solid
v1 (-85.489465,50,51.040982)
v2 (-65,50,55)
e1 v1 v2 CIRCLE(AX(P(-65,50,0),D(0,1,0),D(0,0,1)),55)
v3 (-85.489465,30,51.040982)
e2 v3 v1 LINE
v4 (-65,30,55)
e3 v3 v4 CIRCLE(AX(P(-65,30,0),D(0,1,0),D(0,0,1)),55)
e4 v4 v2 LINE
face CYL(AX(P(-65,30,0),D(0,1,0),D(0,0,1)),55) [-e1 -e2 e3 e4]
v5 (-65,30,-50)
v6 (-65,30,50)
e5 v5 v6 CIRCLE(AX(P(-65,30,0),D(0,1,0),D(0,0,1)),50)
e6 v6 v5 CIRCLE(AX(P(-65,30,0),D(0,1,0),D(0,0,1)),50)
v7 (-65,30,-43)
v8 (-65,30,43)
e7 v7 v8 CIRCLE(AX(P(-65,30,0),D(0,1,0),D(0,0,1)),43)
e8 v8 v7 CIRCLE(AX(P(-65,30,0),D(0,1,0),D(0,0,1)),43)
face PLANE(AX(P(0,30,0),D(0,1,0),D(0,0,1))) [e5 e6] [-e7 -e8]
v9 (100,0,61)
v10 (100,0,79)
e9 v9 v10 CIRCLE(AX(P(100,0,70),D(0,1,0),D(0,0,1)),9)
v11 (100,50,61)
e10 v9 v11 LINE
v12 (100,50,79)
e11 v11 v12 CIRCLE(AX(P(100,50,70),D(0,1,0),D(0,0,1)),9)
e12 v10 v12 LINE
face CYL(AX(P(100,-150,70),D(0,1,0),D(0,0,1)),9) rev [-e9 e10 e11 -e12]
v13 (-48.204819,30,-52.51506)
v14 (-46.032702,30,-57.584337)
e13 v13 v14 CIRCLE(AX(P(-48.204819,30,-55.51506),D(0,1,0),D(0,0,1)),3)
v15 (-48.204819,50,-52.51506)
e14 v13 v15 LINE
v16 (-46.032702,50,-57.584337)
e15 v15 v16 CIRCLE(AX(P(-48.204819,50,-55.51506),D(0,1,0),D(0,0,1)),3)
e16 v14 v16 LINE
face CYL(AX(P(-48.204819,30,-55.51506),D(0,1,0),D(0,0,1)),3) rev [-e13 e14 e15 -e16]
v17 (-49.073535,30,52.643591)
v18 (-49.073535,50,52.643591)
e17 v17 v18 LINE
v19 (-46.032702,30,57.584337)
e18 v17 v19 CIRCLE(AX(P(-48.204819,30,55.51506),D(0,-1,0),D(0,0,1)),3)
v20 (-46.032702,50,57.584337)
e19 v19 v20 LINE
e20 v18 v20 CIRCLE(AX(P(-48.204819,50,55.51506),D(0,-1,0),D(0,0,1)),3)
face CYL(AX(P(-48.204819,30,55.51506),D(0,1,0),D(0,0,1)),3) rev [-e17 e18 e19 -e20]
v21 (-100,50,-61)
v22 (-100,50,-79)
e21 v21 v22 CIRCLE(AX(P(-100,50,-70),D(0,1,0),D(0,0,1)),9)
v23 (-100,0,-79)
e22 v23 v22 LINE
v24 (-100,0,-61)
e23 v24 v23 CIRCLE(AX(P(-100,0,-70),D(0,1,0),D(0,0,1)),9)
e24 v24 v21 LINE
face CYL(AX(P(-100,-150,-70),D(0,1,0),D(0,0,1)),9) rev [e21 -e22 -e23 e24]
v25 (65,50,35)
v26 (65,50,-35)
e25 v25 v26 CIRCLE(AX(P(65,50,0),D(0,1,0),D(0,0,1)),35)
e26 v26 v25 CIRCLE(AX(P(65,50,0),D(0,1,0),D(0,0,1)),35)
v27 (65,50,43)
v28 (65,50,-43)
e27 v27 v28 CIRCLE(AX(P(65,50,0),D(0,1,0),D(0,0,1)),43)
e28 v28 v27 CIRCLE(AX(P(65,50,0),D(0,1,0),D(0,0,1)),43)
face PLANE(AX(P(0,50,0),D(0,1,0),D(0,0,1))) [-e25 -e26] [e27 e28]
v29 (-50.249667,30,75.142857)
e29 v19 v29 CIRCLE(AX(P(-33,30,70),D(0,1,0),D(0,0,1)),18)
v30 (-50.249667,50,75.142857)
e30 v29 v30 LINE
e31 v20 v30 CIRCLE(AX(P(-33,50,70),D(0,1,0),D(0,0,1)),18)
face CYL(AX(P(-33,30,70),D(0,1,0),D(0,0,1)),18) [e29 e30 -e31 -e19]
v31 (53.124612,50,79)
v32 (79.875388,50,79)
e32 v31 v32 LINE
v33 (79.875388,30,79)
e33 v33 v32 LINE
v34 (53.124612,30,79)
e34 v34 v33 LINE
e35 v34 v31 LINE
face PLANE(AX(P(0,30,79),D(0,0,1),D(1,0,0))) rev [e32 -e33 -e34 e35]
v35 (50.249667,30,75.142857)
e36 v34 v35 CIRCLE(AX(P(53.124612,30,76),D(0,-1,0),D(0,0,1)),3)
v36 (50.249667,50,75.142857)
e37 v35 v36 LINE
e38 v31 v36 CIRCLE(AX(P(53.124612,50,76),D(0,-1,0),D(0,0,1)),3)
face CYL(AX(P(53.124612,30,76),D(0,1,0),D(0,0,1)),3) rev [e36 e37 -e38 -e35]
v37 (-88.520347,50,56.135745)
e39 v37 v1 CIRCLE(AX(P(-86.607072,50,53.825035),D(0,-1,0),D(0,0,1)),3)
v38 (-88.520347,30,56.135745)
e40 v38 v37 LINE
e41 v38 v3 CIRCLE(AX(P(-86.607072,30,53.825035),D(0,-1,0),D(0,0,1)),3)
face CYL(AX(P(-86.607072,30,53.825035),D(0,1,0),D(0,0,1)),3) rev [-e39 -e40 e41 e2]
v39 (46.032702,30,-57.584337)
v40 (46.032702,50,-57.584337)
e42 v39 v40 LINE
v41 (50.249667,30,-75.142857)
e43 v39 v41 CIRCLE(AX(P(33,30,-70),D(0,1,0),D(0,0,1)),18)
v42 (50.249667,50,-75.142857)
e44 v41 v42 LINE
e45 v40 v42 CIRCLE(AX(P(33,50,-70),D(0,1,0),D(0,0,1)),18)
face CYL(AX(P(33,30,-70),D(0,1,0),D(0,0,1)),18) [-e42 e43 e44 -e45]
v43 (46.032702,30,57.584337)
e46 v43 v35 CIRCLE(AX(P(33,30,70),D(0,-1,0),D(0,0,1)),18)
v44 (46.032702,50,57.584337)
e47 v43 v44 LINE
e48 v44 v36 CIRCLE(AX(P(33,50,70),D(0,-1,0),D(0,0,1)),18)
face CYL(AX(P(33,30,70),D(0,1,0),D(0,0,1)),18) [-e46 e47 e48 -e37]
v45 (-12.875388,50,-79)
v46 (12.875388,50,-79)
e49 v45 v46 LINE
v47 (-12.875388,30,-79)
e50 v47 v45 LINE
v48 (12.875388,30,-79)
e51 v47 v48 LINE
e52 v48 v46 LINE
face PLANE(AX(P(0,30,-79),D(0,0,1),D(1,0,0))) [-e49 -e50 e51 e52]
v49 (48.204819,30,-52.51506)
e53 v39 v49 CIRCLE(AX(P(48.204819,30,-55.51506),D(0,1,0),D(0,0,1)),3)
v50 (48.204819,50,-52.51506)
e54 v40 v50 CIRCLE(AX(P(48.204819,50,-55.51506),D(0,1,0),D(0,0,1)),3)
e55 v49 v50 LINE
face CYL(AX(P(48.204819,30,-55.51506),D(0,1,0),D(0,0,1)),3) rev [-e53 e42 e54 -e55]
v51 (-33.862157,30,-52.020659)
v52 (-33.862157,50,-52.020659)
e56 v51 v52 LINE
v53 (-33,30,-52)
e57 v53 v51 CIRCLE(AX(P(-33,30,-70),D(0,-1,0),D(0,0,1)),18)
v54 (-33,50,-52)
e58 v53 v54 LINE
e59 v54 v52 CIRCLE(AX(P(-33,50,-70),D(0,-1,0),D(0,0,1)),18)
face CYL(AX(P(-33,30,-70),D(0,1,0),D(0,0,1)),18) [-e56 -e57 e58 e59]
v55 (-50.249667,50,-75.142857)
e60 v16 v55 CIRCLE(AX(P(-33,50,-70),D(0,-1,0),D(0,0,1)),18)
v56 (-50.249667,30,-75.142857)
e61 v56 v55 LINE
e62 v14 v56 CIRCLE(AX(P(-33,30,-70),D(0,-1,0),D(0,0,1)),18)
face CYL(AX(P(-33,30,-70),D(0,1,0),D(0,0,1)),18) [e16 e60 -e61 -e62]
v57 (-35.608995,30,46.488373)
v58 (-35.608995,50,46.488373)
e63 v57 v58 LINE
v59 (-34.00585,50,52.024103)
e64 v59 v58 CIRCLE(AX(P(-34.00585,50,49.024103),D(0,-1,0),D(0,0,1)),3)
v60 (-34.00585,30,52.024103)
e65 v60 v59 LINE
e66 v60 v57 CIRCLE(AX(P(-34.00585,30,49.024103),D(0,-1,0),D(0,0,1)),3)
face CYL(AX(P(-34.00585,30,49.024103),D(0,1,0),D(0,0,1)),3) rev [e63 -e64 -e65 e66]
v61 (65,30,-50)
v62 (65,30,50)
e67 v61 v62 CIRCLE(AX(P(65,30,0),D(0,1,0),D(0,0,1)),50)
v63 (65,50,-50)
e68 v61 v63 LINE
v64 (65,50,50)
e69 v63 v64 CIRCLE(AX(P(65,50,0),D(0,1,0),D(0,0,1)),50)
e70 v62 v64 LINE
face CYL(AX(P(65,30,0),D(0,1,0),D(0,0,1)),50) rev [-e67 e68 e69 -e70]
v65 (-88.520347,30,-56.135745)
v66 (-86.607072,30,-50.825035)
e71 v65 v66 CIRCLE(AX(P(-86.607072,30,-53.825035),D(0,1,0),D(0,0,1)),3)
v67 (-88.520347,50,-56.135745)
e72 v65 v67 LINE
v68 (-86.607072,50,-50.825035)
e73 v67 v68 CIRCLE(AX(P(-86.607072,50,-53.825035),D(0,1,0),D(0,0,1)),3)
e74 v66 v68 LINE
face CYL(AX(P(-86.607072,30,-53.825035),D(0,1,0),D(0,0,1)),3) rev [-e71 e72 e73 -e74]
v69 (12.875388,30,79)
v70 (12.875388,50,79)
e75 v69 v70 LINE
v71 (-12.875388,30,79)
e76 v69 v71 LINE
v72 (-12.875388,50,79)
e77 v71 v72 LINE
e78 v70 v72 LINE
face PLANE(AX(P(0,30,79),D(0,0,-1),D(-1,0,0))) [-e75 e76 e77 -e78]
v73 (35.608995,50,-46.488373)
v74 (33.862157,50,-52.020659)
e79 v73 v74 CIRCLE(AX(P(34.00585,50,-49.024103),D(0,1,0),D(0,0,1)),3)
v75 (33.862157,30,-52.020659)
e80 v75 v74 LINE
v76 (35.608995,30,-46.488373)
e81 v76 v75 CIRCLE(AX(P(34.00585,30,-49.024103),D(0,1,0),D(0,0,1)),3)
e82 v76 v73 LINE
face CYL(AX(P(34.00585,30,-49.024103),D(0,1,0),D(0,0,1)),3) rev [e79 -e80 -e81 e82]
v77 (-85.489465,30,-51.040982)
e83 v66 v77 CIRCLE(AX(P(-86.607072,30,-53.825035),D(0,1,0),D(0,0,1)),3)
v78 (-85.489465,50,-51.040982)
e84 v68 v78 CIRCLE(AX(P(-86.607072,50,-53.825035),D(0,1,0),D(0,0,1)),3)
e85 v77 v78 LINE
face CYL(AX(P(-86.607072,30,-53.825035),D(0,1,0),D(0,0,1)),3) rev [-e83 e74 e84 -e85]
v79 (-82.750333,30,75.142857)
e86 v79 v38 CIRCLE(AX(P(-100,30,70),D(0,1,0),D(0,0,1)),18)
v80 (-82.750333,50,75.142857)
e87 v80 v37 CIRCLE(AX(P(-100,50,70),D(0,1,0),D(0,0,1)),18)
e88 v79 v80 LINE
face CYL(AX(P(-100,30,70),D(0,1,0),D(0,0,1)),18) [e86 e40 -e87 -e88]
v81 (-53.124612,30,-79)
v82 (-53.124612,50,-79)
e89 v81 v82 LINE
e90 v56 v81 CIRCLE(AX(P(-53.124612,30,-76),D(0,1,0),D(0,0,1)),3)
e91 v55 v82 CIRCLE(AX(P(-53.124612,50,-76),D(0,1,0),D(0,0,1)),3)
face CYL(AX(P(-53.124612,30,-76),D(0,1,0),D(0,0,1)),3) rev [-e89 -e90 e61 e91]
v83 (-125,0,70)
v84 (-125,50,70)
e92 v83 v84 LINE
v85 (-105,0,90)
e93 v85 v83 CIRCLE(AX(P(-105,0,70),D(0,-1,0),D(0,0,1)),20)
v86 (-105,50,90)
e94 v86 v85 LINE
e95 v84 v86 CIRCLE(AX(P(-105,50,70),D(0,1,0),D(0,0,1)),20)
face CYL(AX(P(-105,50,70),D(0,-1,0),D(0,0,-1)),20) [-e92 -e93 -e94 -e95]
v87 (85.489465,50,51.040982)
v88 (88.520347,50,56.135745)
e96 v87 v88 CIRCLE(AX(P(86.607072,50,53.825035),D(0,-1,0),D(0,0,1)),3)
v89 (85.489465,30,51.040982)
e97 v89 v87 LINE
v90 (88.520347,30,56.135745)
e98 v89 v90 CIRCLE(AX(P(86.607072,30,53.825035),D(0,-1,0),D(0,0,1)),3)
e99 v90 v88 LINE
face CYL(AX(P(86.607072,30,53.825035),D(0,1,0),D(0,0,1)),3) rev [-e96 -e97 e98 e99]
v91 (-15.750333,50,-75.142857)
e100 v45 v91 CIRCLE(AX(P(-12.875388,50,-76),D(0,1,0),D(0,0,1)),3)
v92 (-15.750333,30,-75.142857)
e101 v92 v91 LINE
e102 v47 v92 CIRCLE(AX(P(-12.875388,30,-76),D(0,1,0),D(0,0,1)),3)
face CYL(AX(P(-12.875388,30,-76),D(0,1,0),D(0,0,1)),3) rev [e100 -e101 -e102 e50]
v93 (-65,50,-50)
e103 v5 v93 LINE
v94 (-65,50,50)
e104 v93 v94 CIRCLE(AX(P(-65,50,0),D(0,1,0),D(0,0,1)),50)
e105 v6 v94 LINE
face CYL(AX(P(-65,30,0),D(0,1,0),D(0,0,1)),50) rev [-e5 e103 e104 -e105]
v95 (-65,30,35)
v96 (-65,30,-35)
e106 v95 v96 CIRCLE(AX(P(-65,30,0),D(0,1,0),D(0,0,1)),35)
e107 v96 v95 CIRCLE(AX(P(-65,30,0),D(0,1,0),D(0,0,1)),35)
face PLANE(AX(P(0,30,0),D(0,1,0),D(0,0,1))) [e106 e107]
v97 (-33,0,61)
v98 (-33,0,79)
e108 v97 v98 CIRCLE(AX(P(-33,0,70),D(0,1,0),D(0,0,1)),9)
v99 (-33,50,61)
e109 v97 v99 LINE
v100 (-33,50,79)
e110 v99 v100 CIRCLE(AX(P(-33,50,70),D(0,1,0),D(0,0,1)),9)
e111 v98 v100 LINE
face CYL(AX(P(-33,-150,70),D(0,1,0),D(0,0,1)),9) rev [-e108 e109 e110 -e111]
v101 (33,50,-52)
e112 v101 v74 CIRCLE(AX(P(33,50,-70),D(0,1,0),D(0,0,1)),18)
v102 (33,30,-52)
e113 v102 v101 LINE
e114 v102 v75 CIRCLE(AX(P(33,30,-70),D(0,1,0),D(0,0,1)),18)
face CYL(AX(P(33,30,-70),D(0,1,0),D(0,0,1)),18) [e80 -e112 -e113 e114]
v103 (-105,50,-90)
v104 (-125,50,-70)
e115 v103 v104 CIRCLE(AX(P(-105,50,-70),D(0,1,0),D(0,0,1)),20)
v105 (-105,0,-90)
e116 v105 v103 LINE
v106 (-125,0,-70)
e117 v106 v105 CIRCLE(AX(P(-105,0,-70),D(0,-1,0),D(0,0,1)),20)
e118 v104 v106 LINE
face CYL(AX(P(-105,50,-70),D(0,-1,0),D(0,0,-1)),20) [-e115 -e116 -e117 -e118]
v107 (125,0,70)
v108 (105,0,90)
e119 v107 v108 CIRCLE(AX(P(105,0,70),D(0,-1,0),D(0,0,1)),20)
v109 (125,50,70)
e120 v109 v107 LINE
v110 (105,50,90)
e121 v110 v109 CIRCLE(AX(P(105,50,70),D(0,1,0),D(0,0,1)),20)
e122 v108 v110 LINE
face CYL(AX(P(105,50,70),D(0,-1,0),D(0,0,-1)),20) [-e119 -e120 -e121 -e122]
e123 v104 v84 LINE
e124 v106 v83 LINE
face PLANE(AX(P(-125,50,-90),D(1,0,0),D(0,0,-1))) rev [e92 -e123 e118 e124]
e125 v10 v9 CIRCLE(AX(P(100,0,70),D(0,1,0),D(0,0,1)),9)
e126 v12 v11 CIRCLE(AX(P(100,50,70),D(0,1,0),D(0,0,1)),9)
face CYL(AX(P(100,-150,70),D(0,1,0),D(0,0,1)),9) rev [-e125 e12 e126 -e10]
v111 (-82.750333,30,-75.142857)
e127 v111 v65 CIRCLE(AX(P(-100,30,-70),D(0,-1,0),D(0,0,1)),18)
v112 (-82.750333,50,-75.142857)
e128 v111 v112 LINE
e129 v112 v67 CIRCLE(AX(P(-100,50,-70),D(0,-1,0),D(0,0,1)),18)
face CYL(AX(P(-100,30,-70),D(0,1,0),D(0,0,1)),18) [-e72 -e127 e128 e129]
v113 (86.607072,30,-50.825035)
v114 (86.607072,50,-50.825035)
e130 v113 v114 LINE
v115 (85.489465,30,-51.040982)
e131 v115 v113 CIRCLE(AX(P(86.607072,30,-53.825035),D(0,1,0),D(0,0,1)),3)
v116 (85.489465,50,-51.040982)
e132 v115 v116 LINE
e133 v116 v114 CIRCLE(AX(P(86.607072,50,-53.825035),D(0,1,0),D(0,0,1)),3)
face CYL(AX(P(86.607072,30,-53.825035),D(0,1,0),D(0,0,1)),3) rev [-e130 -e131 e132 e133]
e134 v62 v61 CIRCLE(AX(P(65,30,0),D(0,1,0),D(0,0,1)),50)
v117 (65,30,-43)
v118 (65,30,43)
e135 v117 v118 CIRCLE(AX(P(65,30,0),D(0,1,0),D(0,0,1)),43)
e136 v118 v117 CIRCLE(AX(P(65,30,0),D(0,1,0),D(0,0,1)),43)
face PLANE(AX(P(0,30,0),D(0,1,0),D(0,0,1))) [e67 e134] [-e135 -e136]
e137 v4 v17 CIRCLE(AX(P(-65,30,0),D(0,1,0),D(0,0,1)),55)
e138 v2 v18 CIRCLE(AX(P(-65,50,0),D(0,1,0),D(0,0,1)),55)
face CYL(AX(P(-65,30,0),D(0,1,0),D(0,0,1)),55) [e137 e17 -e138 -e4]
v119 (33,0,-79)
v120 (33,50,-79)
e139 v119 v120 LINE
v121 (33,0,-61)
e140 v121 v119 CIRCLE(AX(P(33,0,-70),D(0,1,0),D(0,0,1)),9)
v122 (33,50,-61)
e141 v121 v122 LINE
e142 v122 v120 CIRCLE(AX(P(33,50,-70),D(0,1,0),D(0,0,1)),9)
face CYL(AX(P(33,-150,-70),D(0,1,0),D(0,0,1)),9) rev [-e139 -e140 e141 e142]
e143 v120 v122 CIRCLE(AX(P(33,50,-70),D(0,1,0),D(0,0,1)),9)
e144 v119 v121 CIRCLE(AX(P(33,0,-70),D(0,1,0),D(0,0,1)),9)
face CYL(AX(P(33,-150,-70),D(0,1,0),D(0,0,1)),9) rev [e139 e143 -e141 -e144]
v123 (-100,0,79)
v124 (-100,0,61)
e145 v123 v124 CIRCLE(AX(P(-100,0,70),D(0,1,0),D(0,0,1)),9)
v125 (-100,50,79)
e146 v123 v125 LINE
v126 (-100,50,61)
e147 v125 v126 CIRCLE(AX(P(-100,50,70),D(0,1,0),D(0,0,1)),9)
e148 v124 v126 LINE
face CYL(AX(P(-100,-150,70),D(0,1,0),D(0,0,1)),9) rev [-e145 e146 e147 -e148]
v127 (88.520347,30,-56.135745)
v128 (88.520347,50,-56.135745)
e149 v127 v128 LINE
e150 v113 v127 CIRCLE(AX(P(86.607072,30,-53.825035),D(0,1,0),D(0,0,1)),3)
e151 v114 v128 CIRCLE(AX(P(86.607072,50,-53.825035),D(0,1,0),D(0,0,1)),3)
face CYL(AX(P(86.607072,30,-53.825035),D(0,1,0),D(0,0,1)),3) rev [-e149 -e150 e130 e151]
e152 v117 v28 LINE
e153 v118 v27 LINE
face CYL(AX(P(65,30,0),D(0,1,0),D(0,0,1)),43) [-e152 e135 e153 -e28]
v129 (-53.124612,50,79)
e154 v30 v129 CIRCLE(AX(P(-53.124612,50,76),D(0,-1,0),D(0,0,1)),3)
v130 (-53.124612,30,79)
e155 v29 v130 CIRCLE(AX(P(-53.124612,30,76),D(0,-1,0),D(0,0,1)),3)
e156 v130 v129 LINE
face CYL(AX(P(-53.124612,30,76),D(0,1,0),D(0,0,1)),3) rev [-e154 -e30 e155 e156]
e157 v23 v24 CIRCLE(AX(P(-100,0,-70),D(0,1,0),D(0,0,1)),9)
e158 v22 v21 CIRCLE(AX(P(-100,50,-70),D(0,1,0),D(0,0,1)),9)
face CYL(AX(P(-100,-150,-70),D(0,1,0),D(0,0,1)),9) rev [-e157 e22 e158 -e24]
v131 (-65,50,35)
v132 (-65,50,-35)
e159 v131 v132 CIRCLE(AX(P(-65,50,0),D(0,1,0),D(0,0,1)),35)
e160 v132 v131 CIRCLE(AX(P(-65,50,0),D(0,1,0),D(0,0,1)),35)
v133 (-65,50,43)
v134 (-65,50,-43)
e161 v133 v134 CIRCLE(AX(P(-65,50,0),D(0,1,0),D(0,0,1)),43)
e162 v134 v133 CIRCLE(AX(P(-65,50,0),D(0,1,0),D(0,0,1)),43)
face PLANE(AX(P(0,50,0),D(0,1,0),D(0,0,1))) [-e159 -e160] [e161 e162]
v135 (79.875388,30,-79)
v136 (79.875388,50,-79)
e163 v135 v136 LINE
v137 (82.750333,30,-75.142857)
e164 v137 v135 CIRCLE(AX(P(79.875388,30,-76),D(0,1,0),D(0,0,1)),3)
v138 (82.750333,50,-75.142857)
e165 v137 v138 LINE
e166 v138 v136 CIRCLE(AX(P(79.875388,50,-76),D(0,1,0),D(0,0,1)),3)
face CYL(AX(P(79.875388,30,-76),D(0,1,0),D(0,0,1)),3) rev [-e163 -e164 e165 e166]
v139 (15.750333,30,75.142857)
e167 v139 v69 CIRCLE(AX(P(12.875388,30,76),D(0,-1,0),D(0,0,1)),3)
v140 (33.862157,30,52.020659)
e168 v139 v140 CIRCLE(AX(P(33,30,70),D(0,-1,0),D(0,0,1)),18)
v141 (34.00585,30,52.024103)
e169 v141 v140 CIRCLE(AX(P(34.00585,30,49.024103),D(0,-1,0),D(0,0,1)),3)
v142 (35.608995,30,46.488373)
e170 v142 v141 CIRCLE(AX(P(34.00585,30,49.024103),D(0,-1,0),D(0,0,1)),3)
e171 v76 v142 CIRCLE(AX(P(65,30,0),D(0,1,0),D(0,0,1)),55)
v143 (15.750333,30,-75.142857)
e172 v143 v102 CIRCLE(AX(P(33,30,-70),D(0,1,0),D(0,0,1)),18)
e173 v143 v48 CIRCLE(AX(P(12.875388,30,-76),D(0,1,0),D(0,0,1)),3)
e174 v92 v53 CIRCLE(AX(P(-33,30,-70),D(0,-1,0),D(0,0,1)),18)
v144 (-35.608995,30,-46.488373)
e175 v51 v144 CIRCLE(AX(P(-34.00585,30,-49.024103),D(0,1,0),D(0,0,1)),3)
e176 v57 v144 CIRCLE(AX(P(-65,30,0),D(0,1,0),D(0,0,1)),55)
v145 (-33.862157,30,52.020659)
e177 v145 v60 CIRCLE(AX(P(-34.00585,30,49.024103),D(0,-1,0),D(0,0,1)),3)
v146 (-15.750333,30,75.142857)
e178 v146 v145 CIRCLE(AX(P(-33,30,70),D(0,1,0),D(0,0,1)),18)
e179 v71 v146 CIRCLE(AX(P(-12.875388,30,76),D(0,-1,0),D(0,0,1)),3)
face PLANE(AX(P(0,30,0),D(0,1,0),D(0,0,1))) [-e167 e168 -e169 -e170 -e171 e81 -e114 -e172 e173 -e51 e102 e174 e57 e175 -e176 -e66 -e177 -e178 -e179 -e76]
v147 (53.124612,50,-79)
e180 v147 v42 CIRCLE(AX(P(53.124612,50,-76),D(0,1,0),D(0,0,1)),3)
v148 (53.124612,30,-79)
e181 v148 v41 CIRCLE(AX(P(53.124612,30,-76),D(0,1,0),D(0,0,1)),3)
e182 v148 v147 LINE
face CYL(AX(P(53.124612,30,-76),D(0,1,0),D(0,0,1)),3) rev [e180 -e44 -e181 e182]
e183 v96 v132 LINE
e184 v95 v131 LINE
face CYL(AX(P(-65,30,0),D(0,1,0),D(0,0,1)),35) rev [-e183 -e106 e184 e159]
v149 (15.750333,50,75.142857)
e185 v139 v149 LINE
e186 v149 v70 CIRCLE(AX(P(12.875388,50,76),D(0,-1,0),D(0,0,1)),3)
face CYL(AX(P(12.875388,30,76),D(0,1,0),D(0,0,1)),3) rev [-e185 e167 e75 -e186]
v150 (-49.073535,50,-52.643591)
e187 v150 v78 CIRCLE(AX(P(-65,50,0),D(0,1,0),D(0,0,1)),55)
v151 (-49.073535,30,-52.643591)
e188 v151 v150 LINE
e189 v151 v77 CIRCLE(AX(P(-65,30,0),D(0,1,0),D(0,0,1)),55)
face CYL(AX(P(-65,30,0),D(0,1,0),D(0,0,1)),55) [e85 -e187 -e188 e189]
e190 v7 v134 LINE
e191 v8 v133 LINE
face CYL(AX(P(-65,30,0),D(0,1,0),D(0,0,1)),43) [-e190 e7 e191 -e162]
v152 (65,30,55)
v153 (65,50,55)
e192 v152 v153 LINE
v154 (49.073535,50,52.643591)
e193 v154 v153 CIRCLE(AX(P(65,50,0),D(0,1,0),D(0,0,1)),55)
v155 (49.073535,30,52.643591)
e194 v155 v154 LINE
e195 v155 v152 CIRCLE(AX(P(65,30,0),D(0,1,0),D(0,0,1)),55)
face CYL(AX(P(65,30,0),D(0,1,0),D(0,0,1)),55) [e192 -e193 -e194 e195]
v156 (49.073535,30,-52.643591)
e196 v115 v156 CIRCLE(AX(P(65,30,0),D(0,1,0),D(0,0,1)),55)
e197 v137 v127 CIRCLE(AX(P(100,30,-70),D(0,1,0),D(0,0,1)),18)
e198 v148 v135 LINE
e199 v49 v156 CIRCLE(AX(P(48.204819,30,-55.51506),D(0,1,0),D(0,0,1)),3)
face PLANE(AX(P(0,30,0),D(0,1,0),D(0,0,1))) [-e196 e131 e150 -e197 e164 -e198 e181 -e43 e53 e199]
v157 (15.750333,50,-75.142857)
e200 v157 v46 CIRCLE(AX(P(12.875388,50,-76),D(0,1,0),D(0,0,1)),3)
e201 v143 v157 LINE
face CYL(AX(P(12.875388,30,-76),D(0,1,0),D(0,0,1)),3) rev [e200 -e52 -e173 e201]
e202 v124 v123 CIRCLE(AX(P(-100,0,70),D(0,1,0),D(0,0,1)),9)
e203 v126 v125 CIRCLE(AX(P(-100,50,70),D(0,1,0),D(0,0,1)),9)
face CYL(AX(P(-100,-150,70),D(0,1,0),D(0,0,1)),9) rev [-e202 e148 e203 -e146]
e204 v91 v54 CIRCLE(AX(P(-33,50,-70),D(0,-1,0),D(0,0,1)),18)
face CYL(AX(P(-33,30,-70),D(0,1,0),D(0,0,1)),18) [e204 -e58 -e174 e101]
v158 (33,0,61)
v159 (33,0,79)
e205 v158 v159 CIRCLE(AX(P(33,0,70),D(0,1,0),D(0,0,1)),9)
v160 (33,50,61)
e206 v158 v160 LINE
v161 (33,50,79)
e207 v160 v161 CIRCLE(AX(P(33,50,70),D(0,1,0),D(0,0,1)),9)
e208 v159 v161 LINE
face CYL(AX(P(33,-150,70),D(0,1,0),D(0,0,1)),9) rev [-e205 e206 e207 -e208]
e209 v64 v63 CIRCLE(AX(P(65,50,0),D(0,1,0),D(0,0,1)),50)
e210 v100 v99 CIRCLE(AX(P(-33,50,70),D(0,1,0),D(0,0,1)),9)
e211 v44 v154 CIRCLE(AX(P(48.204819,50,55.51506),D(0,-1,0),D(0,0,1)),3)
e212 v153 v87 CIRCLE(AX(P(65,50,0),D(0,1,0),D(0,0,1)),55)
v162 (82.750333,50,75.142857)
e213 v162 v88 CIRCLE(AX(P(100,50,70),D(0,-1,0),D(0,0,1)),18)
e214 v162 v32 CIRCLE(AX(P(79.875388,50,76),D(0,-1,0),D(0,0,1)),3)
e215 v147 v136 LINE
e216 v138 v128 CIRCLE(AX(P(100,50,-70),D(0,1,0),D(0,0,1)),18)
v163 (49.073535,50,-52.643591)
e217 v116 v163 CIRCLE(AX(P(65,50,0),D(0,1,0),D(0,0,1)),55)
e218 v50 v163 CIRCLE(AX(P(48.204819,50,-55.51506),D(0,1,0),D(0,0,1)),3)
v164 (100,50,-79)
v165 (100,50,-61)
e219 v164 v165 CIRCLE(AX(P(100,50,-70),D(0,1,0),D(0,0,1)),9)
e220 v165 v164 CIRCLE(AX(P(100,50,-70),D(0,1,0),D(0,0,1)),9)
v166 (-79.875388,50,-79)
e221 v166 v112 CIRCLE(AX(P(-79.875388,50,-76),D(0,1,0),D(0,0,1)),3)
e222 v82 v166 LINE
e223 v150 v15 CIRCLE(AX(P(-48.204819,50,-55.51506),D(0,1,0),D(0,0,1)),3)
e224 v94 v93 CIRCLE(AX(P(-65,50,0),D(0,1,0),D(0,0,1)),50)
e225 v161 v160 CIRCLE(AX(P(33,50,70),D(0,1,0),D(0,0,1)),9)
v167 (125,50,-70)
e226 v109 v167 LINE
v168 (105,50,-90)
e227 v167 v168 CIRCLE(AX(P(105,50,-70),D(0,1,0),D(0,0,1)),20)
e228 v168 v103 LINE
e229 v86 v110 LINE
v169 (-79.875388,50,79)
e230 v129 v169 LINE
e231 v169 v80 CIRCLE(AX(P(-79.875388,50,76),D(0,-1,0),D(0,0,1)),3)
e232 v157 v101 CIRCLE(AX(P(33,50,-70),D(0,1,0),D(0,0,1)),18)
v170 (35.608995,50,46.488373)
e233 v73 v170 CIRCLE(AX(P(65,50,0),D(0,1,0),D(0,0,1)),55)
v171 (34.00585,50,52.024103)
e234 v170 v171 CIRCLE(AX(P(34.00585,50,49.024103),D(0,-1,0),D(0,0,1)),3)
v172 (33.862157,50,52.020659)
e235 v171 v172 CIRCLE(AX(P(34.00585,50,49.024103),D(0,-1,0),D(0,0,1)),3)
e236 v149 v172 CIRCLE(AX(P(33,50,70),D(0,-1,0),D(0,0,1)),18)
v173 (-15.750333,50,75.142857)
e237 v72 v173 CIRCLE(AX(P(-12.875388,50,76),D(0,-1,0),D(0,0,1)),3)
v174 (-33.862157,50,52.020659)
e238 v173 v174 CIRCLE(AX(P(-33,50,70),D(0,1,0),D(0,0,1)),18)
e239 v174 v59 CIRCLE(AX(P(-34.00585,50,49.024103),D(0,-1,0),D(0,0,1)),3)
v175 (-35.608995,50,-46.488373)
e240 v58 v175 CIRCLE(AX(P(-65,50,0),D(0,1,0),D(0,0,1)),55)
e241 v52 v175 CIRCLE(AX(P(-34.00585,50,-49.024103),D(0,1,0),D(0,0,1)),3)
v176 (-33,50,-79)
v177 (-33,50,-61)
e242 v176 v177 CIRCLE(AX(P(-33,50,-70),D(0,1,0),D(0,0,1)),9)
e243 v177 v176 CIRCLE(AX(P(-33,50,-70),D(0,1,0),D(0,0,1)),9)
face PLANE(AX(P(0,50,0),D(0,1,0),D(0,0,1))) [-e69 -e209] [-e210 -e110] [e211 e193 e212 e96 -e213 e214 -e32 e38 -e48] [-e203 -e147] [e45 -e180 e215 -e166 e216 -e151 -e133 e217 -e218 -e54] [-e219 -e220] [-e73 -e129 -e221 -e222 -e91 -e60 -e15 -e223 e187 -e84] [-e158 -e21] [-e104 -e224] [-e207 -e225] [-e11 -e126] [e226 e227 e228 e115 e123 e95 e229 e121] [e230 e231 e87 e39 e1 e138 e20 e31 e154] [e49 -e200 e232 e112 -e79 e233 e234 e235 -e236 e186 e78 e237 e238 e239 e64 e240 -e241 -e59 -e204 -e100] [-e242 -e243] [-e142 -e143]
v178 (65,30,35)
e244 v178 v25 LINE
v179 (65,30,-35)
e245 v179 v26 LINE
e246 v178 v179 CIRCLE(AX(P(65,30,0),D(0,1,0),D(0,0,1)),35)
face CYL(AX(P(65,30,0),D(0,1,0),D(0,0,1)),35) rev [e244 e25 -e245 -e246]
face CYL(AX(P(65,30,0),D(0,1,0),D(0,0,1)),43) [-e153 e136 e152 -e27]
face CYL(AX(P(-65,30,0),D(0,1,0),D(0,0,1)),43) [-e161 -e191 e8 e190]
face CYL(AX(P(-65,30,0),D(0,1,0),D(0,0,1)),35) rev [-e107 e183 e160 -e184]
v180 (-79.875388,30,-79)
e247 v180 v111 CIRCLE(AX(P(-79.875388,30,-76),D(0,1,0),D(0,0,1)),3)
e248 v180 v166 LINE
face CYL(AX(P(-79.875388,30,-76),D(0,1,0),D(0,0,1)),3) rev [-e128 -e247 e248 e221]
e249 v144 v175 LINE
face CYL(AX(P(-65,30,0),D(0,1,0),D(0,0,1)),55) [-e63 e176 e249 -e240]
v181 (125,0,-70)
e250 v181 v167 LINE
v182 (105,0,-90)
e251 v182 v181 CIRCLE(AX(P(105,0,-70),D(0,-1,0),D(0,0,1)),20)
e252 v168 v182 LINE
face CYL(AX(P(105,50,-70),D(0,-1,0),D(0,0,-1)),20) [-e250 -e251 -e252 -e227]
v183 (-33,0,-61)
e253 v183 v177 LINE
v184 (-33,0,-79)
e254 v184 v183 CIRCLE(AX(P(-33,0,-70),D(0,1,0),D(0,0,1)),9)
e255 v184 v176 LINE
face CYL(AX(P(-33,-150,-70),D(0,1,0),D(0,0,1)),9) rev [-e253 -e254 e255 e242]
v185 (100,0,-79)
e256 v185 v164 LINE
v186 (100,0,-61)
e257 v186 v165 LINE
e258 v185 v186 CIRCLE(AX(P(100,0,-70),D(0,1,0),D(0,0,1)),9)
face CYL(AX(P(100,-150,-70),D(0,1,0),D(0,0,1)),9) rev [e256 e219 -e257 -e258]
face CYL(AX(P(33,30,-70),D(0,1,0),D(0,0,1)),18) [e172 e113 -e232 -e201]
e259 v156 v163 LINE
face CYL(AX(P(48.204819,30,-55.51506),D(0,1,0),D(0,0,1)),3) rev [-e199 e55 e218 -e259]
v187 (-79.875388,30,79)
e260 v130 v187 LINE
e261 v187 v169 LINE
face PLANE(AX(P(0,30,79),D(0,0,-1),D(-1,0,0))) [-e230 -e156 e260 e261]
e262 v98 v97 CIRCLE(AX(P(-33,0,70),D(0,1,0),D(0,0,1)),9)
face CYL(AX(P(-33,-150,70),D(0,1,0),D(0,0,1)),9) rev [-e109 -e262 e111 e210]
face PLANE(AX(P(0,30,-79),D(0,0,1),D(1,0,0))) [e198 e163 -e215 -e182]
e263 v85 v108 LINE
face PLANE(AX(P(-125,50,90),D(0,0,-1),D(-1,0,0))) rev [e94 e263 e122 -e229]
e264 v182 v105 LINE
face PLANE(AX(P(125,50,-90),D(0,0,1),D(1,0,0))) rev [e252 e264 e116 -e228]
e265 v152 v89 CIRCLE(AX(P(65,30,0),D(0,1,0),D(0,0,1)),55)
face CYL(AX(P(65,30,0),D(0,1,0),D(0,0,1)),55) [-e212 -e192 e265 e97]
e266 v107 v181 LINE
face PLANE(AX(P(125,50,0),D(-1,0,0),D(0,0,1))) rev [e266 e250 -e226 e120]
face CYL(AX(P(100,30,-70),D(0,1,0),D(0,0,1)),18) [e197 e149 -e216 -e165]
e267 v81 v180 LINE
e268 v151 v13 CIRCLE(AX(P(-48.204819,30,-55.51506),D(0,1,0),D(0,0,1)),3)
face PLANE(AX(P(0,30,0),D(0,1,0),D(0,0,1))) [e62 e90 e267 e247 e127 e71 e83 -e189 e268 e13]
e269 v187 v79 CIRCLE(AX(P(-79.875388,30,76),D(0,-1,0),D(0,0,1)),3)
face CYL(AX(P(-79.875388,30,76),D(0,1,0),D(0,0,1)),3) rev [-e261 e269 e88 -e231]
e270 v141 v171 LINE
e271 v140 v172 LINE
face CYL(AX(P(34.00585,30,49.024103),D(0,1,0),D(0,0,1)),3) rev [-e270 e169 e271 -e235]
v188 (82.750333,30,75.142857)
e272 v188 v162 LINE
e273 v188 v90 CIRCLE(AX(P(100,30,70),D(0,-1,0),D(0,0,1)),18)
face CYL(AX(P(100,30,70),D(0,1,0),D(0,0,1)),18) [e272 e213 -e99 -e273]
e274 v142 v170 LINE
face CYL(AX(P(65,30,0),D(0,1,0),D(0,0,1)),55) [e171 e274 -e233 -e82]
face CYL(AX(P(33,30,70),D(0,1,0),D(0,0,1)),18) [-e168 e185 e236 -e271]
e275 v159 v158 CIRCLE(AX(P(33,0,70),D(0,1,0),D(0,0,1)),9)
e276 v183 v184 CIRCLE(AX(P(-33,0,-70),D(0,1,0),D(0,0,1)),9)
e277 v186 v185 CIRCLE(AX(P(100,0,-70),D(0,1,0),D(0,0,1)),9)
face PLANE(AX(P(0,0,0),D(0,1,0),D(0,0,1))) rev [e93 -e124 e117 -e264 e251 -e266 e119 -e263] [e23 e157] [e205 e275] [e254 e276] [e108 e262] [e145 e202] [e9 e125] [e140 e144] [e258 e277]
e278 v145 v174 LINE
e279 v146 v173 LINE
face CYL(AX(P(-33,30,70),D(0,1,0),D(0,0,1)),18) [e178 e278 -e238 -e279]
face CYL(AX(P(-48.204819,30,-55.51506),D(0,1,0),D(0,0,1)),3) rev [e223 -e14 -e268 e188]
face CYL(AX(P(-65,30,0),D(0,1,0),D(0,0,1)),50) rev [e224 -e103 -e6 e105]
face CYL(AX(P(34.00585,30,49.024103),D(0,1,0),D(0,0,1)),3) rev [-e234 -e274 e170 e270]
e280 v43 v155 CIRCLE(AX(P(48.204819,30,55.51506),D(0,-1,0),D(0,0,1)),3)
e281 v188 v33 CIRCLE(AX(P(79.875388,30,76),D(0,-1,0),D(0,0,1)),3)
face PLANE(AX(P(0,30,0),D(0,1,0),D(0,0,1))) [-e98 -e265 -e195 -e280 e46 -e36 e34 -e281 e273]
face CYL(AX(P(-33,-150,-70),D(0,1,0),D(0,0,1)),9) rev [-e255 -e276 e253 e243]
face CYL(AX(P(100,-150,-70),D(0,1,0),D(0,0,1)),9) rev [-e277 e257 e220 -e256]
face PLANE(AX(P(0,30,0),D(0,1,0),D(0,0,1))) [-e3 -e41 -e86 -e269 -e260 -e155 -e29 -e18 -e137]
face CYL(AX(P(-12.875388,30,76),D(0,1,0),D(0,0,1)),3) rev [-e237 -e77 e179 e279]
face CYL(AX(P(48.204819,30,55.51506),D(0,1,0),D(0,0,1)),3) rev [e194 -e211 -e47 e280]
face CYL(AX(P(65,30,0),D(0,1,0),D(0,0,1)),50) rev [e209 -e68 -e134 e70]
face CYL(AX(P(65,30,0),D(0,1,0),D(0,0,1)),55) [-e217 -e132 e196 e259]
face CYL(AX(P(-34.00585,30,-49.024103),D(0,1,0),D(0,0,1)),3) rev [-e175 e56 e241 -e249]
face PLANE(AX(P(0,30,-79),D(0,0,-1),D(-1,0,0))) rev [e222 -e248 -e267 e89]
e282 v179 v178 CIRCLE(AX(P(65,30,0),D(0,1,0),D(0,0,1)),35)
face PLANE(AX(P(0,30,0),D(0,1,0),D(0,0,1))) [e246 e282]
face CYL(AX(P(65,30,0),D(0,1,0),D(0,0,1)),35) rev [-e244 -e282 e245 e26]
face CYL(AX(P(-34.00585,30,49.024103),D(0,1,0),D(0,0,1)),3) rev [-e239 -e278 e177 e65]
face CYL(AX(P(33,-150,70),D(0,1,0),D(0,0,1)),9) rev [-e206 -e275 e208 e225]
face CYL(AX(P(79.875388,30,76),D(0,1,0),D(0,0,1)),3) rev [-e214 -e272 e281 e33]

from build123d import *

# Parameters (mm, degrees)
BASE_PLATE_250X180X50_DEPTH          = 50
BORE_SEATS_AND_POCKETS_PROFILE_R     = 50
BORE_SEATS_AND_POCKETS_PROFILE_R_2   = 43
BORE_SEATS_AND_POCKETS_PROFILE_R_3   = 35
BORE_SEATS_AND_POCKETS_20_DEEP_DEPTH = 20
BOLT_HOLES_PROFILE_R                 = 9
BOLT_HOLES_8X_18_DEPTH               = 200
CORNER_ROUND_R20_A_R                 = 20
CORNER_ROUND_R20_B_R                 = 20
CORNER_ROUND_R20_C_R                 = 20
CORNER_ROUND_R20_D_R                 = 20


with BuildPart() as part:
    # Base Plate Profile → Base Plate 250x180x50 (new body)
    with BuildSketch(Plane(origin=(0, 0, 0), x_dir=(1, 0, 0), z_dir=(0, 1, 0))):
        Polygon((125, 0), (125, 90), (-125, 90), (-125, -90), (125, -90), align=None)
    extrude(amount=BASE_PLATE_250X180X50_DEPTH)

    # Bore Seats and Pockets Profile → Bore Seats and Pockets 20 Deep (cut)
    # profile 1 of 9: a face of its own
    with BuildSketch(Plane(origin=(0, 50, 0), x_dir=(1, 0, 0), z_dir=(0, 1, 0))):
        with BuildLine():
            ThreePointArc((85.489464765, 51.040981903), (67.418125523, 54.946816732), (49.07353502, 52.643591379))
            ThreePointArc((49.07353502, 52.643591379), (45.649930196, 53.942627335), (46.032701785, 57.584337142))
            ThreePointArc((46.032701785, 57.584337142), (50.502310556, 65.796534146), (50.249667255, 75.142857143))
            ThreePointArc((50.249667255, 75.142857143), (50.71926062, 77.792842914), (53.124611797, 79))
            Line((53.124611797, 79), (79.875388203, 79))
            ThreePointArc((79.875388203, 79), (82.28073938, 77.792842914), (82.750332745, 75.142857143))
            ThreePointArc((82.750332745, 75.142857143), (82.776149203, 64.771332509), (88.520347372, 56.135744681))
            ThreePointArc((88.520347372, 56.135744681), (89.185331801, 52.291224502), (85.489464765, 51.040981903))
        make_face()
    # profile 2 of 9: a face of its own
    with BuildSketch(Plane(origin=(0, 50, 0), x_dir=(1, 0, 0), z_dir=(0, 1, 0))):
        with BuildLine():
            ThreePointArc((-35.608995423, -46.488373277), (-10, 0), (-35.608995423, 46.488373277))
            ThreePointArc((-35.608995423, 46.488373277), (-36.866627296, 49.927403152), (-33.862156902, 52.020659482))
            ThreePointArc((-33.862156902, 52.020659482), (-18.829727241, 58.900298656), (-15.750332745, 75.142857143))
            ThreePointArc((-15.750332745, 75.142857143), (-15.28073938, 77.792842914), (-12.875388203, 79))
            Line((-12.875388203, 79), (0, 79))
            Line((0, 79), (12.875388203, 79))
            ThreePointArc((12.875388203, 79), (15.28073938, 77.792842914), (15.750332745, 75.142857143))
            ThreePointArc((15.750332745, 75.142857143), (18.829727241, 58.900298656), (33.862156902, 52.020659482))
            ThreePointArc((33.862156902, 52.020659482), (36.866627296, 49.927403152), (35.608995423, 46.488373277))
            ThreePointArc((35.608995423, 46.488373277), (10, 0), (35.608995423, -46.488373277))
            ThreePointArc((35.608995423, -46.488373277), (36.866627296, -49.927403152), (33.862156902, -52.020659482))
            ThreePointArc((33.862156902, -52.020659482), (18.829727241, -58.900298656), (15.750332745, -75.142857143))
            ThreePointArc((15.750332745, -75.142857143), (15.28073938, -77.792842914), (12.875388203, -79))
            Line((12.875388203, -79), (0, -79))
            Line((0, -79), (-12.875388203, -79))
            ThreePointArc((-12.875388203, -79), (-15.28073938, -77.792842914), (-15.750332745, -75.142857143))
            ThreePointArc((-15.750332745, -75.142857143), (-18.829727241, -58.900298656), (-33.862156902, -52.020659482))
            ThreePointArc((-33.862156902, -52.020659482), (-36.866627296, -49.927403152), (-35.608995423, -46.488373277))
        make_face()
    # profile 3 of 9: a face of its own
    with BuildSketch(Plane(origin=(0, 50, 0), x_dir=(1, 0, 0), z_dir=(0, 1, 0))):
        with BuildLine():
            ThreePointArc((-49.07353502, 52.643591379), (-67.418125523, 54.946816732), (-85.489464765, 51.040981903))
            ThreePointArc((-85.489464765, 51.040981903), (-89.185331801, 52.291224502), (-88.520347372, 56.135744681))
            ThreePointArc((-88.520347372, 56.135744681), (-82.776149203, 64.771332509), (-82.750332745, 75.142857143))
            ThreePointArc((-82.750332745, 75.142857143), (-82.28073938, 77.792842914), (-79.875388203, 79))
            Line((-79.875388203, 79), (-53.124611797, 79))
            ThreePointArc((-53.124611797, 79), (-50.71926062, 77.792842914), (-50.249667255, 75.142857143))
            ThreePointArc((-50.249667255, 75.142857143), (-50.502310556, 65.796534146), (-46.032701785, 57.584337142))
            ThreePointArc((-46.032701785, 57.584337142), (-45.649930196, 53.942627335), (-49.07353502, 52.643591379))
        make_face()
    # profile 4 of 9: a face of its own
    with BuildSketch(Plane(origin=(0, 50, 0), x_dir=(1, 0, 0), z_dir=(0, 1, 0))):
        with BuildLine():
            ThreePointArc((-49.07353502, -52.643591379), (-45.649930196, -53.942627335), (-46.032701785, -57.584337142))
            ThreePointArc((-46.032701785, -57.584337142), (-50.502310556, -65.796534146), (-50.249667255, -75.142857143))
            ThreePointArc((-50.249667255, -75.142857143), (-50.71926062, -77.792842914), (-53.124611797, -79))
            Line((-53.124611797, -79), (-79.875388203, -79))
            ThreePointArc((-79.875388203, -79), (-82.28073938, -77.792842914), (-82.750332745, -75.142857143))
            ThreePointArc((-82.750332745, -75.142857143), (-82.776149203, -64.771332509), (-88.520347372, -56.135744681))
            ThreePointArc((-88.520347372, -56.135744681), (-89.185331801, -52.291224502), (-85.489464765, -51.040981903))
            ThreePointArc((-85.489464765, -51.040981903), (-67.418125523, -54.946816732), (-49.07353502, -52.643591379))
        make_face()
    # profile 5 of 9: a face of its own
    with BuildSketch(Plane(origin=(0, 50, 0), x_dir=(1, 0, 0), z_dir=(0, 1, 0))):
        with BuildLine():
            ThreePointArc((49.07353502, -52.643591379), (67.418125523, -54.946816732), (85.489464765, -51.040981903))
            ThreePointArc((85.489464765, -51.040981903), (89.185331801, -52.291224502), (88.520347372, -56.135744681))
            ThreePointArc((88.520347372, -56.135744681), (82.776149203, -64.771332509), (82.750332745, -75.142857143))
            ThreePointArc((82.750332745, -75.142857143), (82.28073938, -77.792842914), (79.875388203, -79))
            Line((79.875388203, -79), (53.124611797, -79))
            ThreePointArc((53.124611797, -79), (50.71926062, -77.792842914), (50.249667255, -75.142857143))
            ThreePointArc((50.249667255, -75.142857143), (50.502310556, -65.796534146), (46.032701785, -57.584337142))
            ThreePointArc((46.032701785, -57.584337142), (45.649930196, -53.942627335), (49.07353502, -52.643591379))
        make_face()
    # profile 6 of 9: a face of its own
    with BuildSketch(Plane(origin=(0, 50, 0), x_dir=(1, 0, 0), z_dir=(0, 1, 0))):
        with Locations(Location((65, 0, 0), (0, 0, 270))):
            Circle(BORE_SEATS_AND_POCKETS_PROFILE_R)
        with Locations(Location((65, 0, 0), (0, 0, 270))):
            Circle(BORE_SEATS_AND_POCKETS_PROFILE_R_2, mode=Mode.SUBTRACT)
    # profile 7 of 9: a face of its own
    with BuildSketch(Plane(origin=(0, 50, 0), x_dir=(1, 0, 0), z_dir=(0, 1, 0))):
        with Locations(Location((65, 0, 0), (0, 0, 270))):
            Circle(BORE_SEATS_AND_POCKETS_PROFILE_R_3)
    # profile 8 of 9: a face of its own
    with BuildSketch(Plane(origin=(0, 50, 0), x_dir=(1, 0, 0), z_dir=(0, 1, 0))):
        with Locations(Location((-65, 0, 0), (0, 0, 270))):
            Circle(BORE_SEATS_AND_POCKETS_PROFILE_R)
        with Locations(Location((-65, 0, 0), (0, 0, 270))):
            Circle(BORE_SEATS_AND_POCKETS_PROFILE_R_2, mode=Mode.SUBTRACT)
    # profile 9 of 9: a face of its own
    with BuildSketch(Plane(origin=(0, 50, 0), x_dir=(1, 0, 0), z_dir=(0, 1, 0))):
        with Locations(Location((-65, 0, 0), (0, 0, 270))):
            Circle(BORE_SEATS_AND_POCKETS_PROFILE_R_3)
    extrude(amount=-BORE_SEATS_AND_POCKETS_20_DEEP_DEPTH, mode=Mode.SUBTRACT)

    # Bolt Holes Profile → Bolt Holes 8xØ18 (cut)
    with BuildSketch(Plane(origin=(0, 50, 0), x_dir=(1, 0, 0), z_dir=(0, 1, 0))):
        with Locations(Location((100, -70, 0), (0, 0, 270))):
            Circle(BOLT_HOLES_PROFILE_R)
        with Locations(Location((33, -70, 0), (0, 0, 270))):
            Circle(BOLT_HOLES_PROFILE_R)
        with Locations(Location((-33, -70, 0), (0, 0, 270))):
            Circle(BOLT_HOLES_PROFILE_R)
        with Locations(Location((-100, -70, 0), (0, 0, 270))):
            Circle(BOLT_HOLES_PROFILE_R)
        with Locations(Location((-100, 70, 0), (0, 0, 270))):
            Circle(BOLT_HOLES_PROFILE_R)
        with Locations(Location((-33, 70, 0), (0, 0, 270))):
            Circle(BOLT_HOLES_PROFILE_R)
        with Locations(Location((33, 70, 0), (0, 0, 270))):
            Circle(BOLT_HOLES_PROFILE_R)
        with Locations(Location((100, 70, 0), (0, 0, 270))):
            Circle(BOLT_HOLES_PROFILE_R)
    extrude(amount=-BOLT_HOLES_8X_18_DEPTH, mode=Mode.SUBTRACT)

    # Corner Round R20 A
    corner_round_r20_a_edges = [part.edges().sort_by_distance(p)[0] for p in [
        (-125, 25, 90),
    ]]
    fillet(corner_round_r20_a_edges, radius=CORNER_ROUND_R20_A_R)

    # Corner Round R20 B
    corner_round_r20_b_edges = [part.edges().sort_by_distance(p)[0] for p in [
        (-125, 25, -90),
    ]]
    fillet(corner_round_r20_b_edges, radius=CORNER_ROUND_R20_B_R)

    # Corner Round R20 C
    corner_round_r20_c_edges = [part.edges().sort_by_distance(p)[0] for p in [
        (125, 25, -90),
    ]]
    fillet(corner_round_r20_c_edges, radius=CORNER_ROUND_R20_C_R)

    # Corner Round R20 D
    corner_round_r20_d_edges = [part.edges().sort_by_distance(p)[0] for p in [
        (125, 25, 90),
    ]]
    fillet(corner_round_r20_d_edges, radius=CORNER_ROUND_R20_D_R)


solid = part.part
